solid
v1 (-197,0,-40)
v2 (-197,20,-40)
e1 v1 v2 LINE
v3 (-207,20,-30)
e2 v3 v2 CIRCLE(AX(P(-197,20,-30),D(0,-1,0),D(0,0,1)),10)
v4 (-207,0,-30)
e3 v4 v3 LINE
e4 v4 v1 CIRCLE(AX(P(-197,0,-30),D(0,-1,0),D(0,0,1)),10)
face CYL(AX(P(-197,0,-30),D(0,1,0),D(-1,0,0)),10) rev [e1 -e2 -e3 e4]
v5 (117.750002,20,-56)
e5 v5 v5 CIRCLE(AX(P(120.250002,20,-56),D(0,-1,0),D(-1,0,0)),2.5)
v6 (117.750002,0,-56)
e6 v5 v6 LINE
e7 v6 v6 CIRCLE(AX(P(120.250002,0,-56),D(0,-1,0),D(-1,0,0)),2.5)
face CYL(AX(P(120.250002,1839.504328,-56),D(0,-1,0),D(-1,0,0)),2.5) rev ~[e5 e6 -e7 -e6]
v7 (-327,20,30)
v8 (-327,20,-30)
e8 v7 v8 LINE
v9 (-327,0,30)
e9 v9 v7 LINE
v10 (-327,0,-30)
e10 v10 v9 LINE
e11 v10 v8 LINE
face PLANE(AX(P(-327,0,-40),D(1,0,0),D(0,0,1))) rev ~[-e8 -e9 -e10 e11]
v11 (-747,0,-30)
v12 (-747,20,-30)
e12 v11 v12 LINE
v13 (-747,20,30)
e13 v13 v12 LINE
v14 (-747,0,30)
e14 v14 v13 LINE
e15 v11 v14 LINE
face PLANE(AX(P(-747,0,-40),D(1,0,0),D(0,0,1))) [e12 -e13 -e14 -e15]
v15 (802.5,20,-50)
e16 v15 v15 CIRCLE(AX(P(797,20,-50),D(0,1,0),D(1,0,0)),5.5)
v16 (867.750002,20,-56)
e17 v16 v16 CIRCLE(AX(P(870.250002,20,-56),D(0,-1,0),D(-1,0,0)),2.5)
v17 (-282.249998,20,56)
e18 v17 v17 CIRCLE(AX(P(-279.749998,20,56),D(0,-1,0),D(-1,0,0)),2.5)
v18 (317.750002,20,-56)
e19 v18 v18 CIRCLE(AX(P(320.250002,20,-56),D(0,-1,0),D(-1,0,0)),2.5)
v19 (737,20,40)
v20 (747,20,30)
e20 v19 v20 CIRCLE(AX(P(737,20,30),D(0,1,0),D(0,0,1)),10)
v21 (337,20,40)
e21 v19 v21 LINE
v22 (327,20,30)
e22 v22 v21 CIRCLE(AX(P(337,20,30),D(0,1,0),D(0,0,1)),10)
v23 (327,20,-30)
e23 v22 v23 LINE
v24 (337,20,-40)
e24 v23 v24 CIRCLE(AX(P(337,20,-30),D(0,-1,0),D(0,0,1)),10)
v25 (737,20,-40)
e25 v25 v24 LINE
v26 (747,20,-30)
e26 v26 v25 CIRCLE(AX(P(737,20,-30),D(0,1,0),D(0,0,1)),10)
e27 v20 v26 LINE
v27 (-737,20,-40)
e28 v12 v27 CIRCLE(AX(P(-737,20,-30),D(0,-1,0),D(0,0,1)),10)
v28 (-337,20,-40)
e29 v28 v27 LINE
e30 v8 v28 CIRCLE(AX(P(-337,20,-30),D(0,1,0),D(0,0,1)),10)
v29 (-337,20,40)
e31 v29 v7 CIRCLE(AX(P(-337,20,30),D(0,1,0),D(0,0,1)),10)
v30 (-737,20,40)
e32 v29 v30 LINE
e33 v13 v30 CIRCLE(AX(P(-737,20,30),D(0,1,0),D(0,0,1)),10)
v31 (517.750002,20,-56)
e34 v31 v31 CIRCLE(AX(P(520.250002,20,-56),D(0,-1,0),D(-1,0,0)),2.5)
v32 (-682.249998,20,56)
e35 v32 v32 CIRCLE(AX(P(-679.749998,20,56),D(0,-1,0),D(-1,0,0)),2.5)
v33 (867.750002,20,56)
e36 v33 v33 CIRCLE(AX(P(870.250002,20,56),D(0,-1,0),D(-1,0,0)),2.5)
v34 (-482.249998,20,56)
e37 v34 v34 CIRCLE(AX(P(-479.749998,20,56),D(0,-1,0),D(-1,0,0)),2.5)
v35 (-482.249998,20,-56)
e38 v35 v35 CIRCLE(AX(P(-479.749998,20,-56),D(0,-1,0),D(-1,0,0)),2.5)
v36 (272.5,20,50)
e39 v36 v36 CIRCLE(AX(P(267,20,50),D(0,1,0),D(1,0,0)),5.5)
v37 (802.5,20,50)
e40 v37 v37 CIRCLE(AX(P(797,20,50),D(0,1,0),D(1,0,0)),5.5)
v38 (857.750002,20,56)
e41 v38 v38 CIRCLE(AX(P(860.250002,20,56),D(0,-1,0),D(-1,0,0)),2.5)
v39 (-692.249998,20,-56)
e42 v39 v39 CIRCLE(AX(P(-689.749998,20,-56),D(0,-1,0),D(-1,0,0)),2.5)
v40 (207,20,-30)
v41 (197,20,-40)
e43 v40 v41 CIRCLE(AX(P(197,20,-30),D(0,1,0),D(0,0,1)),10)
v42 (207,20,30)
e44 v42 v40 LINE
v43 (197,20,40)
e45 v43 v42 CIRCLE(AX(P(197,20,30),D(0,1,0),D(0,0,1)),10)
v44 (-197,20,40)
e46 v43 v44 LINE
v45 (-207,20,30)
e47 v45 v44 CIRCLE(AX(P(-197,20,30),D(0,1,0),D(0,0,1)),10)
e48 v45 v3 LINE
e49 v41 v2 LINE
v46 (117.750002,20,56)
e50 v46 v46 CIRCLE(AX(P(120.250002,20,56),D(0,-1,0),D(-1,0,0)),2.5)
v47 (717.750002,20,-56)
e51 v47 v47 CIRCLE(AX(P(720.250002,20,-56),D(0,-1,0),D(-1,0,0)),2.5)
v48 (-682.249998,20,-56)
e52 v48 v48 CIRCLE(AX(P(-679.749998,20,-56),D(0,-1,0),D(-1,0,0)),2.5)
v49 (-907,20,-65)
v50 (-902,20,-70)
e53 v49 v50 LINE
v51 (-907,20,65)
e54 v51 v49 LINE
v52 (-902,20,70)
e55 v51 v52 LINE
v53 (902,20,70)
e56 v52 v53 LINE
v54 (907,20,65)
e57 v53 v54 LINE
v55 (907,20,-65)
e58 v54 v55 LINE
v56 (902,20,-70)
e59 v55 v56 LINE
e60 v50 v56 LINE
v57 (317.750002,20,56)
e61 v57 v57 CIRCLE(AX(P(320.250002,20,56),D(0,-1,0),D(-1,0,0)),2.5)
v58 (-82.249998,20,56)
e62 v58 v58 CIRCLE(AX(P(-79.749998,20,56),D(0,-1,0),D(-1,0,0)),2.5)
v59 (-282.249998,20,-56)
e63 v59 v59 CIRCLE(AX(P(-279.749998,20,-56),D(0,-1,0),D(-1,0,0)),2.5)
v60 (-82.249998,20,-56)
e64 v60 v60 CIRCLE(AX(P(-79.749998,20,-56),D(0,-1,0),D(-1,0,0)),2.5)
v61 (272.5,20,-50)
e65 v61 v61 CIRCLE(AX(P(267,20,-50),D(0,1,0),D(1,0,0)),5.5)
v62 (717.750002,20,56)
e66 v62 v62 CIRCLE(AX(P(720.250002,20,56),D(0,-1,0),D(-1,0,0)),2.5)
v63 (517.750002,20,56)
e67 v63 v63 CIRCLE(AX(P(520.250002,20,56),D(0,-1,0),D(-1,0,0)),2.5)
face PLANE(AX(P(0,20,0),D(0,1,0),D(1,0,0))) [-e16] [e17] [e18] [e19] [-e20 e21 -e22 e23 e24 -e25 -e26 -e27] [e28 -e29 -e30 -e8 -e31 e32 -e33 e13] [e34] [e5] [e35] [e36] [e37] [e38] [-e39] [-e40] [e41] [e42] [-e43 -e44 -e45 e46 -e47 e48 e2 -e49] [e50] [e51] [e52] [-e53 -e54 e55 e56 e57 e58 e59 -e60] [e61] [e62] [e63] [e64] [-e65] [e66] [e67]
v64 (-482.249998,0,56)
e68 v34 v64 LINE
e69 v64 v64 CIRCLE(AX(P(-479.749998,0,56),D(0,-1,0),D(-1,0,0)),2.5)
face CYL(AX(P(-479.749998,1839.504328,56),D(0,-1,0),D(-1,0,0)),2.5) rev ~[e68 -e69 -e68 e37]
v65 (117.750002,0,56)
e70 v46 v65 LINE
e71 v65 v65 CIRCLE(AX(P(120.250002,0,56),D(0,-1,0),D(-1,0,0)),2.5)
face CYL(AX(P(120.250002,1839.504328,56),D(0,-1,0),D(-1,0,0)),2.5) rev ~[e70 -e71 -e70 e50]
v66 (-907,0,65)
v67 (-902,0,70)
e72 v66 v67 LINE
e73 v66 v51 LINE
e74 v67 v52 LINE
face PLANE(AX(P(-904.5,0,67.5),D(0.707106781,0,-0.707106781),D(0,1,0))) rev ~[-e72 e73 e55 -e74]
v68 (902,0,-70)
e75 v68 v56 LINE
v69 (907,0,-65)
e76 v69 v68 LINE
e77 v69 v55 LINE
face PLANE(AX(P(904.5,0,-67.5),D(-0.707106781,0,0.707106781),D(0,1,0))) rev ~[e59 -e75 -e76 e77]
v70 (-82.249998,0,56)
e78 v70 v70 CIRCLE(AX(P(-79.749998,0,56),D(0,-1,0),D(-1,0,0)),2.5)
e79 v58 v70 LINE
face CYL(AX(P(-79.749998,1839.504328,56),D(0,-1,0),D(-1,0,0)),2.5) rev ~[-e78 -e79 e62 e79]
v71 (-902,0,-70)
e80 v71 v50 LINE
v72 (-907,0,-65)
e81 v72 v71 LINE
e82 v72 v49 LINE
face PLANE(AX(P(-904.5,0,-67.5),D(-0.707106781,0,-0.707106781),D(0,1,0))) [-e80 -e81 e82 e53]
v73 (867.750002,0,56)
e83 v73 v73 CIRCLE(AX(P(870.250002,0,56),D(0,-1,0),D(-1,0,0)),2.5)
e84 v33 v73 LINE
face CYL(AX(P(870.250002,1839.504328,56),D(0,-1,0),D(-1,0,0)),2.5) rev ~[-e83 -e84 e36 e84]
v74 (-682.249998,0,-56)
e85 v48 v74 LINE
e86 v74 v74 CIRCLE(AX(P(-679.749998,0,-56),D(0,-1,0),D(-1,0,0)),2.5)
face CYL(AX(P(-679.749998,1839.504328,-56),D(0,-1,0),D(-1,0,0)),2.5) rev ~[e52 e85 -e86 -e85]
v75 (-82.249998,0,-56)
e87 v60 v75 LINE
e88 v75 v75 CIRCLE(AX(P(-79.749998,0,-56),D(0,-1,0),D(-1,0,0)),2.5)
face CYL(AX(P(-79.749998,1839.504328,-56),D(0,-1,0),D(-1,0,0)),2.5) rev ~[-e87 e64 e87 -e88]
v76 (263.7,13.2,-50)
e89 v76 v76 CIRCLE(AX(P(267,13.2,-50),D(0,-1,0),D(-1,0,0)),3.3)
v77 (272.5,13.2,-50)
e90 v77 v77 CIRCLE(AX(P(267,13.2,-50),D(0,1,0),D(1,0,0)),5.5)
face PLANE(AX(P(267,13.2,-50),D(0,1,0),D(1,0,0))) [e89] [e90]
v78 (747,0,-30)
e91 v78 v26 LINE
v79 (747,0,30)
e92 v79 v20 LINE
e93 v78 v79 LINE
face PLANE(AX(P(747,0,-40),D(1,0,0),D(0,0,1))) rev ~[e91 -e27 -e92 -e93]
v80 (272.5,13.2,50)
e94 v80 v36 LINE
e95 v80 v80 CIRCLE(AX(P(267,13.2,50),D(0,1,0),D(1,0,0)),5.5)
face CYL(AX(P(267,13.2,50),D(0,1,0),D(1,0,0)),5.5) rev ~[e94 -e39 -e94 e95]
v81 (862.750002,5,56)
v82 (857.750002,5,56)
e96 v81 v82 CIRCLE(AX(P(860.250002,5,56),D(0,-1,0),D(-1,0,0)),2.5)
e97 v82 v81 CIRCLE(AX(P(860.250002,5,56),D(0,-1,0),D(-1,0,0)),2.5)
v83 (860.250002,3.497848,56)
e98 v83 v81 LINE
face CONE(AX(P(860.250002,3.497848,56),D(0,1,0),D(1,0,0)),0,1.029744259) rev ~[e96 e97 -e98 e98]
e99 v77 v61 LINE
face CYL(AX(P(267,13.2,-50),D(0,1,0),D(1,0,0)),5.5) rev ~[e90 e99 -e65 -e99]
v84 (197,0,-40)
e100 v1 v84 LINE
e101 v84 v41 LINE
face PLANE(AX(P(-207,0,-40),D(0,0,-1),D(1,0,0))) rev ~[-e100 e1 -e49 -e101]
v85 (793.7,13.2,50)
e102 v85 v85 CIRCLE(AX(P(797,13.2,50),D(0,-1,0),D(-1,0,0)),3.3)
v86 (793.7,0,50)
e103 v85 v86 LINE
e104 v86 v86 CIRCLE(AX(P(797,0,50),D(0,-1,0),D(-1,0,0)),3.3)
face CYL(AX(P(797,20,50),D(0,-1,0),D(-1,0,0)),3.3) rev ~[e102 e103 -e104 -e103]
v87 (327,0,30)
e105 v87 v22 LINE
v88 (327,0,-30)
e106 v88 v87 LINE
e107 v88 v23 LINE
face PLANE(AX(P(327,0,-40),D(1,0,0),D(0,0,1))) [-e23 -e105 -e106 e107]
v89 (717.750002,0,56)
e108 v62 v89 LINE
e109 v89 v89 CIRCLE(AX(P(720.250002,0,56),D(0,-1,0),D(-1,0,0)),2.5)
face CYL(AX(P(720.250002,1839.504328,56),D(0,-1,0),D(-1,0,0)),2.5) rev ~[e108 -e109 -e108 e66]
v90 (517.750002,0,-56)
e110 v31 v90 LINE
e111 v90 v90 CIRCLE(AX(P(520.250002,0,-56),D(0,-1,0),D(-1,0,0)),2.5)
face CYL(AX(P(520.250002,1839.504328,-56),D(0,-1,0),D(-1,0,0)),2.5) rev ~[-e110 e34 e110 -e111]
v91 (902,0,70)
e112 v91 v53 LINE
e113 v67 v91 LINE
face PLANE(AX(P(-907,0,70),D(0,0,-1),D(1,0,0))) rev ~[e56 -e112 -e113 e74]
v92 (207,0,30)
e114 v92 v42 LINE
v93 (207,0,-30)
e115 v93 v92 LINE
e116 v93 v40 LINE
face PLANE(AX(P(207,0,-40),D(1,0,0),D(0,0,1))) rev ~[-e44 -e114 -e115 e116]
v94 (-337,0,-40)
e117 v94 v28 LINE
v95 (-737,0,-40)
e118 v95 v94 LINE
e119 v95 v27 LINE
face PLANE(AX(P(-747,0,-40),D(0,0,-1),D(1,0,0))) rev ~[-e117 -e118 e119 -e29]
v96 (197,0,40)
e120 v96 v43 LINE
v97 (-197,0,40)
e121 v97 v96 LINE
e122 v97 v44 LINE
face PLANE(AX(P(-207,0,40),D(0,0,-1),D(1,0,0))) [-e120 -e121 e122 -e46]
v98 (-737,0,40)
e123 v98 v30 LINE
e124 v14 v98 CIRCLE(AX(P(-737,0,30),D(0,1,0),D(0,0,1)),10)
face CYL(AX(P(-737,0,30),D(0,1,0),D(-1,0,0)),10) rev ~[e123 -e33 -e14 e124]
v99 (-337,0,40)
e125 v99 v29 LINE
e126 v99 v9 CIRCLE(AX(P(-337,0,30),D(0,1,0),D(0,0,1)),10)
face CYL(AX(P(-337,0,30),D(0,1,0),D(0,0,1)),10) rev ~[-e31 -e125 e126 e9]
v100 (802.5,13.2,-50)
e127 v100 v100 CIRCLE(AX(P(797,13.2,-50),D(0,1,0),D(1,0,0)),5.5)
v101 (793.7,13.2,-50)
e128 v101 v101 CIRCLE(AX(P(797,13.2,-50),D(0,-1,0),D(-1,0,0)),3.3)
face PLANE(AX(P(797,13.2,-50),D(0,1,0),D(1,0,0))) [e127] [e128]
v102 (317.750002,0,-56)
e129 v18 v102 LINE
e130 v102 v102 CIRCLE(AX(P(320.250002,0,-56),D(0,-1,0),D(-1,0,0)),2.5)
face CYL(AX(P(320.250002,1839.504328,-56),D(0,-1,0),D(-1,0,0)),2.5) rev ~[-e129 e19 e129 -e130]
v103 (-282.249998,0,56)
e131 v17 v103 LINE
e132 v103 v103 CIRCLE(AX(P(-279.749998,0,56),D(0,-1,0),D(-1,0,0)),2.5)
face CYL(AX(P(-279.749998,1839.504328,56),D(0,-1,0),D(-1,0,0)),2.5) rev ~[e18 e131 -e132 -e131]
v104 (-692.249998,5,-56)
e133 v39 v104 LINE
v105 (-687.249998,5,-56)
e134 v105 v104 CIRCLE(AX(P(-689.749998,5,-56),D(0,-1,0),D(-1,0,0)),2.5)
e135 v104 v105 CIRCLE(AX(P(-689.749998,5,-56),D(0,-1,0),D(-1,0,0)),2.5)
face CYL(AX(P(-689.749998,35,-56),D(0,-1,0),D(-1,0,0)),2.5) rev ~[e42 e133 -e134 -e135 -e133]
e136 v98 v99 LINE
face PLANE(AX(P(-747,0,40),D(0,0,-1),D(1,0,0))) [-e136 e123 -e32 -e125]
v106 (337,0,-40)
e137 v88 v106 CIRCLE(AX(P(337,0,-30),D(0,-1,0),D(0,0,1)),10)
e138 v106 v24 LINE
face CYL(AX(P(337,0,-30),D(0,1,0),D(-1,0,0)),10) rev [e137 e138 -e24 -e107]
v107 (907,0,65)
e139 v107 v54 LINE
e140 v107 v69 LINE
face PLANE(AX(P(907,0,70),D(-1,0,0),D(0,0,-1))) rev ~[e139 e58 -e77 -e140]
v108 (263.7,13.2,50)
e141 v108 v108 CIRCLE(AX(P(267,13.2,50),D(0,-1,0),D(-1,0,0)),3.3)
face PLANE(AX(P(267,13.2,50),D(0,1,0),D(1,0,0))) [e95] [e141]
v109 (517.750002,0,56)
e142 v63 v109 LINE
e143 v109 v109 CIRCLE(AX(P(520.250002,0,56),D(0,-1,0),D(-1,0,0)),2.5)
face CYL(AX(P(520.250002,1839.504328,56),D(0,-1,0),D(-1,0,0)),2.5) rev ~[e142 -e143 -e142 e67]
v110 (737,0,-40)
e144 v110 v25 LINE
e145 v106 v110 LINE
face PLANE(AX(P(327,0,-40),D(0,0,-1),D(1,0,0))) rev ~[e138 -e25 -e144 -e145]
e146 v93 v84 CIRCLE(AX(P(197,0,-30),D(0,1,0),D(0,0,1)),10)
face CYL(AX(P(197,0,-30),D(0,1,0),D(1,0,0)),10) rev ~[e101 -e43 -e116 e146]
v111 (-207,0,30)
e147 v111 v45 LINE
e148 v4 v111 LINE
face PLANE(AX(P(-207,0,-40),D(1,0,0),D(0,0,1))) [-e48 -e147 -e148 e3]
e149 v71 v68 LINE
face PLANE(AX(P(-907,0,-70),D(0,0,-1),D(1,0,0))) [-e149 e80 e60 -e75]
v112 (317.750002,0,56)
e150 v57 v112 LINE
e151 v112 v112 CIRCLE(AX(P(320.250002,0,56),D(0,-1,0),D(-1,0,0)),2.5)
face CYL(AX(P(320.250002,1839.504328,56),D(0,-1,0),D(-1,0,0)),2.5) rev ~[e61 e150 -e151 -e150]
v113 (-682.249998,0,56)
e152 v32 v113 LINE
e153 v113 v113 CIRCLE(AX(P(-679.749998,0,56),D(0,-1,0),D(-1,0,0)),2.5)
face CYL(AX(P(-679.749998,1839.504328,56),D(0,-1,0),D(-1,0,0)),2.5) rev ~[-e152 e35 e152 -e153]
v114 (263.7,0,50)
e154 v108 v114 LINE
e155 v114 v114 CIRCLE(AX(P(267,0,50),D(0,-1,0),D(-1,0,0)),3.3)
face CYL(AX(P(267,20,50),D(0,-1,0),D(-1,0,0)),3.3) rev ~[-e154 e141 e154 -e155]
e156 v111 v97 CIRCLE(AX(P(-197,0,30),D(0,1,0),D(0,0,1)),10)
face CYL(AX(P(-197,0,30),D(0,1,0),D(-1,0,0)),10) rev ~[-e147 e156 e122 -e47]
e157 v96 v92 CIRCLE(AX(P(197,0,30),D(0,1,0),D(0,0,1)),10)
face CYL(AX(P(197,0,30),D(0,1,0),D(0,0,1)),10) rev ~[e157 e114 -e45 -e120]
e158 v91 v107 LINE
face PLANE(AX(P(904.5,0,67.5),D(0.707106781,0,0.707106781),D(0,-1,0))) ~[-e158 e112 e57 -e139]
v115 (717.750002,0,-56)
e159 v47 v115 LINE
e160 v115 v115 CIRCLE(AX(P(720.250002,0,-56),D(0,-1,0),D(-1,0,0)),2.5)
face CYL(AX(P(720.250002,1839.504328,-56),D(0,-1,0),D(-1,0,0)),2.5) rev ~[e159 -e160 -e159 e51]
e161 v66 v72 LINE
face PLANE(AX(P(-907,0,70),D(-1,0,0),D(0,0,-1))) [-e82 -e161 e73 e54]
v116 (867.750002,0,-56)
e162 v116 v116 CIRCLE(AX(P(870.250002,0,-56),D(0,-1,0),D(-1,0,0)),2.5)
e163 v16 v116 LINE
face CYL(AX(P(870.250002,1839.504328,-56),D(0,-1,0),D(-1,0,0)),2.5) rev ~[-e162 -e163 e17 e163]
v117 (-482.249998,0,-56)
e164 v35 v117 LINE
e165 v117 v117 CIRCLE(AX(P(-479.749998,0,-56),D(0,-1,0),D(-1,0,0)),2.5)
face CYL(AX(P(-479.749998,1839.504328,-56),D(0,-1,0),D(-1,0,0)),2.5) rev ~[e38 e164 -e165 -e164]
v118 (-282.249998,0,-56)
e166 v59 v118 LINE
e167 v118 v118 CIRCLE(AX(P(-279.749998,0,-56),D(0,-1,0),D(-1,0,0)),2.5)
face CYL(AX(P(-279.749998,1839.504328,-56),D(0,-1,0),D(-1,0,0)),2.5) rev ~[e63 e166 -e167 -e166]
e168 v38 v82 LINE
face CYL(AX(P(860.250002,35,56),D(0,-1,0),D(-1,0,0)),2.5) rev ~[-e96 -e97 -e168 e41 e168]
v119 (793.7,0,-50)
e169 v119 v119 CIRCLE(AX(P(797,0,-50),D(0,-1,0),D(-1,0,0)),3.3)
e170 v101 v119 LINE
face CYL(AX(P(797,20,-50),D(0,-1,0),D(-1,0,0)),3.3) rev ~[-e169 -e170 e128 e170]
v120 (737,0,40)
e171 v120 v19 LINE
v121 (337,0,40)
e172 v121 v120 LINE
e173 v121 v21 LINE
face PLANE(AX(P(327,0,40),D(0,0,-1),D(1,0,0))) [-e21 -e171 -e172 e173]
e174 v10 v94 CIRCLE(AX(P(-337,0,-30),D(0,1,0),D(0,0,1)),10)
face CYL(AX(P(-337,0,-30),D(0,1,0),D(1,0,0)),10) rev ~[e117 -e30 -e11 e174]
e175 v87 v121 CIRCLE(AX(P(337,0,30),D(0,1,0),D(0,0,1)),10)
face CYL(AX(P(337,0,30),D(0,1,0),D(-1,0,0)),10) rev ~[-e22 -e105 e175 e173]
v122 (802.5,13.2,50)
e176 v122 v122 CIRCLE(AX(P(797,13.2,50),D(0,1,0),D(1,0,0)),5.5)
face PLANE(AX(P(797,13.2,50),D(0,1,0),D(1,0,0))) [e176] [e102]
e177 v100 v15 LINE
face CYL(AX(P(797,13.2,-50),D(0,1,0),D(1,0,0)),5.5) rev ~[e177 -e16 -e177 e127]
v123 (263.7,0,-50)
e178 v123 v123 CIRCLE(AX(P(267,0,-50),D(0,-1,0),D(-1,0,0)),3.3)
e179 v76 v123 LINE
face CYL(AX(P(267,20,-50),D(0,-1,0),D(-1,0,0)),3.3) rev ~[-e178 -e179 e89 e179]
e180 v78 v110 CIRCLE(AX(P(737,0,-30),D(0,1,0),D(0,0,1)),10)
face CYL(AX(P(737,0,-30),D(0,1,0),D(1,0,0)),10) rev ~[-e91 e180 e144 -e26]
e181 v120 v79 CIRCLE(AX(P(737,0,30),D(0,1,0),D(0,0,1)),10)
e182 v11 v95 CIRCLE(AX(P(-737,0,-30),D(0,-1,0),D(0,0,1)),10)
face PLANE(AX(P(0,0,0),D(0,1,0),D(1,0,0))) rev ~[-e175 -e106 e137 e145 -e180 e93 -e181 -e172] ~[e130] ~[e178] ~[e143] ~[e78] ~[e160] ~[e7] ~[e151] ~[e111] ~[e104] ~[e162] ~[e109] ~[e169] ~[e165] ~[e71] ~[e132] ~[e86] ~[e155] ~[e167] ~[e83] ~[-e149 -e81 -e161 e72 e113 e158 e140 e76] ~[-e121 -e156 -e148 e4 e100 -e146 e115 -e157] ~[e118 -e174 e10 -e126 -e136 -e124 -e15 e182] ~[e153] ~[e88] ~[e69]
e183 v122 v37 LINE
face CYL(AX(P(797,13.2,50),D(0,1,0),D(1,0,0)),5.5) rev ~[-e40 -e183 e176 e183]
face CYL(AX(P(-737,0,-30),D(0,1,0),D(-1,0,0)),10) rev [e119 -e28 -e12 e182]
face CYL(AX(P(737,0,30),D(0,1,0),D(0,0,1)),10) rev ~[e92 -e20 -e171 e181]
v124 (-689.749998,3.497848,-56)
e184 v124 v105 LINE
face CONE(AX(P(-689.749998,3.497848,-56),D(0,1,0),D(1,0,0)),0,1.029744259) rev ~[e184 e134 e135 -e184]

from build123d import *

# Parameters (mm, degrees)
SKETCH_1_W                   = 1814
SKETCH_1_H                   = 140
EXTRUDE_1_DEPTH              = 20
CHAMFER_1_SIZE               = 5
HOLE_WIZARD_M6_1_D           = 6.6
HOLE_WIZARD_M6_1_CBORE_D     = 11
HOLE_WIZARD_M6_1_CBORE_DEPTH = 6.8
SKETCH_5_W                   = 420
SKETCH_5_H                   = 80
SKETCH_5_W_2                 = 414
CUT_EXTRUDE_1_DEPTH          = 910.917029185
FILLET_2_R                   = 10
HOLE_WIZARD_M6_1_2_D         = 5
F_5_0MM_1_D                  = 5
F_5_0MM_1_DEPTH              = 15
F_5_0MM_1_TIP                = 1.502151548


with BuildPart() as part:
    # 草图1 → 凸台-拉伸1 (new body)
    with BuildSketch(Plane(origin=(0, 0, 0), x_dir=(1, 0, 0), z_dir=(0, 1, 0))):
        Rectangle(SKETCH_1_W, SKETCH_1_H)
    extrude(amount=EXTRUDE_1_DEPTH)

    # 倒角1
    chamfer_1_edges = [part.edges().sort_by_distance(p)[0] for p in [
        (907, 10, 70),
        (-907, 10, 70),
        (-907, 10, -70),
        (907, 10, -70),
    ]]
    chamfer(chamfer_1_edges, length=CHAMFER_1_SIZE)

    # Hole Wizard M6 _1 (through all)
    with Locations(Plane(origin=(0, 20, 0), x_dir=(1, 0, 0), z_dir=(0, 1, 0))):
        with Locations((267, 50), (797, 50), (797, -50), (267, -50)):
            CounterBoreHole(HOLE_WIZARD_M6_1_D / 2, HOLE_WIZARD_M6_1_CBORE_D / 2, HOLE_WIZARD_M6_1_CBORE_DEPTH)

    # 草图5 → 切除-拉伸1 (cut, through all)
    with BuildSketch(Plane.XZ):
        with Locations((537, 0)):
            Rectangle(SKETCH_5_W, SKETCH_5_H)
        Rectangle(SKETCH_5_W_2, SKETCH_5_H)
        with Locations((-537, 0)):
            Rectangle(SKETCH_5_W, SKETCH_5_H)
    extrude(amount=-CUT_EXTRUDE_1_DEPTH, mode=Mode.SUBTRACT)

    # 圆角2
    fillet_2_edges = [part.edges().sort_by_distance(p)[0] for p in [
        (-747, 10, 40),
        (-327, 10, 40),
        (-327, 10, -40),
        (-747, 10, -40),
        (327, 10, -40),
        (327, 10, 40),
        (747, 10, 40),
        (747, 10, -40),
        (-207, 10, -40),
        (-207, 10, 40),
        (207, 10, 40),
        (207, 10, -40),
    ]]
    fillet(fillet_2_edges, radius=FILLET_2_R)

    # Hole Wizard M6 _1 2 (through all)
    with Locations(Plane(origin=(0, 20, 0), x_dir=(1, 0, 0), z_dir=(0, 1, 0))):
        with Locations((-679.749998444, 56), (-479.749998444, 56), (-279.749998444, 56), (-79.749998444, 56), (120.250001556, 56), (320.250001556, 56), (520.250001556, 56), (720.250001556, 56), (870.250001556, 56), (870.250001556, -56), (720.250001556, -56), (520.250001556, -56), (320.250001556, -56), (120.250001556, -56), (-79.749998444, -56), (-279.749998444, -56), (-479.749998444, -56), (-679.749998444, -56)):
            Hole(HOLE_WIZARD_M6_1_2_D / 2)

    # Ø5.0mm 暗销孔1
    with Locations(Plane(origin=(0, 20, 0), x_dir=(1, 0, 0), z_dir=(0, 1, 0))):
        with Locations((-689.749998444, 56), (860.250001556, -56)):
            Hole(F_5_0MM_1_D / 2, depth=F_5_0MM_1_DEPTH)
            with Locations((0, 0, -(F_5_0MM_1_DEPTH + F_5_0MM_1_TIP / 2))):  # 118° drill point
                Cone(0, F_5_0MM_1_D / 2, F_5_0MM_1_TIP, mode=Mode.SUBTRACT)


solid = part.part
